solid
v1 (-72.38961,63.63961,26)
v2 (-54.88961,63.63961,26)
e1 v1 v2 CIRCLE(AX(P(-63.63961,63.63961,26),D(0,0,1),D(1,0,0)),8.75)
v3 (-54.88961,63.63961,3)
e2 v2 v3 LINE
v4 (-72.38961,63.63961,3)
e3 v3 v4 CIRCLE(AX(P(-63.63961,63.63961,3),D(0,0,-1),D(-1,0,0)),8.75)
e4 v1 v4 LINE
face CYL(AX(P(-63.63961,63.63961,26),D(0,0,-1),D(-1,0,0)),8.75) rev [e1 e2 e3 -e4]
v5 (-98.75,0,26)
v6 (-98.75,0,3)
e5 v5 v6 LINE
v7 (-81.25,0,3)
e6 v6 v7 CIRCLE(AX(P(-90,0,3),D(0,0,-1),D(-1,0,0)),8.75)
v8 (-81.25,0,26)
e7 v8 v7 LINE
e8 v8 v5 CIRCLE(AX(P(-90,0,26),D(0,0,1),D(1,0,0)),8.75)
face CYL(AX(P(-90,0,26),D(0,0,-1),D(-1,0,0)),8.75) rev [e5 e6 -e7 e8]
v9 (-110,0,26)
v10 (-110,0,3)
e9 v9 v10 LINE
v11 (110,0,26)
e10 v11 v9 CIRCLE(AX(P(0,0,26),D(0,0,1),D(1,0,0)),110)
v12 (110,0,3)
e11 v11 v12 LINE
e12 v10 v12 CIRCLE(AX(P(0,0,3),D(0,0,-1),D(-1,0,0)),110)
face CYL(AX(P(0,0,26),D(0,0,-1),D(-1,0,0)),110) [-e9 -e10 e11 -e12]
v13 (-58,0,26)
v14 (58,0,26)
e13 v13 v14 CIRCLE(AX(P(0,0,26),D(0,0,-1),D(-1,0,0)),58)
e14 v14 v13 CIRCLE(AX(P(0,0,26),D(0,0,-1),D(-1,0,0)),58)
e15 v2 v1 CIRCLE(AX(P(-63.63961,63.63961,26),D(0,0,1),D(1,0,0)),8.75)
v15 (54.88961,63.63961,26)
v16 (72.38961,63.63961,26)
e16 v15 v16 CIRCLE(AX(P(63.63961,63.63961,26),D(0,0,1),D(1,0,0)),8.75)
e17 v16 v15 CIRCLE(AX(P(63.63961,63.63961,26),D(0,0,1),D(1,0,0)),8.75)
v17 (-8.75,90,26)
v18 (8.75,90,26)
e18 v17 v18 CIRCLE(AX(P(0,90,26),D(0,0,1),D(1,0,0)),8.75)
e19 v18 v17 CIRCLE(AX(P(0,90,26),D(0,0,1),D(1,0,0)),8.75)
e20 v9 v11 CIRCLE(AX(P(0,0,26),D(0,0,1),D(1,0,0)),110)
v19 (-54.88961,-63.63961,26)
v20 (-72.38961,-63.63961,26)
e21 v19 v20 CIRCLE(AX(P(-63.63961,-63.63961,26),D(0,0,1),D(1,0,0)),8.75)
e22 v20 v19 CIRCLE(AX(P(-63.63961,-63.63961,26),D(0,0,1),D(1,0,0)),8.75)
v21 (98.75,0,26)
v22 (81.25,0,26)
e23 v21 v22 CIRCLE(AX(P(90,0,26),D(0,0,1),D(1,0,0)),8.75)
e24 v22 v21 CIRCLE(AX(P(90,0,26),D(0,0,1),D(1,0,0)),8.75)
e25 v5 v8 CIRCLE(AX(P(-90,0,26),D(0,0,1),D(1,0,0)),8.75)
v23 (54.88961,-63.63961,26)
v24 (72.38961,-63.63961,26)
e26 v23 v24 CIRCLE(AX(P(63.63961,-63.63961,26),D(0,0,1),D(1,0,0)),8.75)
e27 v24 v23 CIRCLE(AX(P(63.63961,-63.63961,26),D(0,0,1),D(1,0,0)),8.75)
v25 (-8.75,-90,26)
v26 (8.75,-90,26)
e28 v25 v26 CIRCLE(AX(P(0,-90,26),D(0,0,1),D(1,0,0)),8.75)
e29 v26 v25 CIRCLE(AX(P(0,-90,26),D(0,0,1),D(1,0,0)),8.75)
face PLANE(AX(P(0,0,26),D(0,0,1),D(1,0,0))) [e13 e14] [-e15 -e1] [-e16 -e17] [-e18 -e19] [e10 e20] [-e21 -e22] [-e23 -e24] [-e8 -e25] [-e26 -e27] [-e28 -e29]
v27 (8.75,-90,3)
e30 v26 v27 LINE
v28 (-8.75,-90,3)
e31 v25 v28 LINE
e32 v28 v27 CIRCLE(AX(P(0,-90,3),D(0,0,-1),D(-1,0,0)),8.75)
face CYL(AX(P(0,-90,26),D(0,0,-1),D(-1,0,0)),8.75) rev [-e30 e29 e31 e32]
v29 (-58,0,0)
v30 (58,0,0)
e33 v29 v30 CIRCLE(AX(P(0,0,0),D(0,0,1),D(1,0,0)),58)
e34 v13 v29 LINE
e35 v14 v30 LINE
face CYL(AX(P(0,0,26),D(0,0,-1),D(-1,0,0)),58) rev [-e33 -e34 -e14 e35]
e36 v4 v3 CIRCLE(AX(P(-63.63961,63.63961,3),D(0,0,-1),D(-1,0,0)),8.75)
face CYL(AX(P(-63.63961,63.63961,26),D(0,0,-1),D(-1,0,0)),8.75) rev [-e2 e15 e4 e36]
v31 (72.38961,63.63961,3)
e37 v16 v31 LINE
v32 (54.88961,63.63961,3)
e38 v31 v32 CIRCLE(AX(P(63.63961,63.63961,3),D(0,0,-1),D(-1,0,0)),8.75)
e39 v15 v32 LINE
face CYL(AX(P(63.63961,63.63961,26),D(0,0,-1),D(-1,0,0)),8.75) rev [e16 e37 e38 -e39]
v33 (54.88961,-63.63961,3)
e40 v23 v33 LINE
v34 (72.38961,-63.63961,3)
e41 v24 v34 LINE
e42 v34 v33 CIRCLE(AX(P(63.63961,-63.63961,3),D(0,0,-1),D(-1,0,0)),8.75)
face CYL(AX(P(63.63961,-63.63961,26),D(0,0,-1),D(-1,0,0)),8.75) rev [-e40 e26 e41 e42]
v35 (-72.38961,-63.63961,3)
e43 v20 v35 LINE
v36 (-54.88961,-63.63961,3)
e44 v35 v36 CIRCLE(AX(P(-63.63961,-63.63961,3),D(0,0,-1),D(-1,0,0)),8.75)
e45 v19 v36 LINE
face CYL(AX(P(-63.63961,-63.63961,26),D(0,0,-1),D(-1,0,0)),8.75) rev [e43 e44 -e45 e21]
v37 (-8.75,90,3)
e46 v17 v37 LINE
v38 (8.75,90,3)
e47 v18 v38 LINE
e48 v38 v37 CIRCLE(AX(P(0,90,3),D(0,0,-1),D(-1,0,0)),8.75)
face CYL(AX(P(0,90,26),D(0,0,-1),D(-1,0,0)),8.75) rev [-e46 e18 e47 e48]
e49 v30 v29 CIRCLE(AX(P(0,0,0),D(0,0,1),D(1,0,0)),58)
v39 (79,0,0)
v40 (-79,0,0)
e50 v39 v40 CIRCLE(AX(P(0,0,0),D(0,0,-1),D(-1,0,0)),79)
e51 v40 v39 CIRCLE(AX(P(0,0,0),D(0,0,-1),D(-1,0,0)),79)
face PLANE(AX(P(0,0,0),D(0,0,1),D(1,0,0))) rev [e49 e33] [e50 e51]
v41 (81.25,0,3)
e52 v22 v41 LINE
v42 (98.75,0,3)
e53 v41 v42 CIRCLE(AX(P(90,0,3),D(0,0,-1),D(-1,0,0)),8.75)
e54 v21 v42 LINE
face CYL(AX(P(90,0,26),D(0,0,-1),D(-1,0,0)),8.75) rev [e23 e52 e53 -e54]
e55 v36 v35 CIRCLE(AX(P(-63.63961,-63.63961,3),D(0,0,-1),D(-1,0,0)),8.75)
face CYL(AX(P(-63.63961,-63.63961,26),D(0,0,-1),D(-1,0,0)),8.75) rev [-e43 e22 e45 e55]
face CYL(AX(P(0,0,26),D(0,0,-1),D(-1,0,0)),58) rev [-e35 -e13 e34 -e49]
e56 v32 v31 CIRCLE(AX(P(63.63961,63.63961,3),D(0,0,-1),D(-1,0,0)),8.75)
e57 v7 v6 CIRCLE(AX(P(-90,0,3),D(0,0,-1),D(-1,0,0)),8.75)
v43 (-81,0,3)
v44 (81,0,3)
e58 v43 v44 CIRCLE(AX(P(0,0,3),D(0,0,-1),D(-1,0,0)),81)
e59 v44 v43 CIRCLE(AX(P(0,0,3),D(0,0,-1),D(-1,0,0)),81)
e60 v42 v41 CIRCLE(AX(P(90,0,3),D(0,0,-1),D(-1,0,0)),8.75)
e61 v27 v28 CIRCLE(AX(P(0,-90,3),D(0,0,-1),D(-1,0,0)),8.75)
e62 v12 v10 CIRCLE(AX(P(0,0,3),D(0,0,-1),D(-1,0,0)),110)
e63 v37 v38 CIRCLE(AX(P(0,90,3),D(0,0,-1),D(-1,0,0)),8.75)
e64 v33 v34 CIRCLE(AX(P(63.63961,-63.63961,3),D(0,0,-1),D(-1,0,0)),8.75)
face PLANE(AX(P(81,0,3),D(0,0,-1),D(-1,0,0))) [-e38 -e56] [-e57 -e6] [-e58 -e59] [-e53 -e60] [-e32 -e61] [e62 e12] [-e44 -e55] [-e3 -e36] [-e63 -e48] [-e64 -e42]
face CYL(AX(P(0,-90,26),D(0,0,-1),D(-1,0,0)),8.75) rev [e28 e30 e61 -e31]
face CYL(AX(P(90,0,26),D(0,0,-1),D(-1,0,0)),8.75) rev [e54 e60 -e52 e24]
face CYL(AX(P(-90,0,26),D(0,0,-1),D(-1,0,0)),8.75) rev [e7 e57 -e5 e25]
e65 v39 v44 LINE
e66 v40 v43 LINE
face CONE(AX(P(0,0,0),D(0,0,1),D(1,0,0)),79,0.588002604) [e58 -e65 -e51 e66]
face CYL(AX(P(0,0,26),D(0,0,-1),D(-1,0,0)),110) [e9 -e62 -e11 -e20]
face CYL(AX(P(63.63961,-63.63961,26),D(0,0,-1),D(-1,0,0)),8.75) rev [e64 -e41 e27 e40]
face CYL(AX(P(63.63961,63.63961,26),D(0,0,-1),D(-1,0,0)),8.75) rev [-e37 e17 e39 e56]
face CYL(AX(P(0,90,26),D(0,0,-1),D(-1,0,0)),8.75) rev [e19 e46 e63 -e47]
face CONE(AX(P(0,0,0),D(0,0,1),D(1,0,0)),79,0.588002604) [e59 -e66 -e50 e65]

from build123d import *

# Parameters (mm, degrees)
SKETCH1_R               = 110
SKETCH1_R_2             = 8.75
BOSS_EXTRUDE1_DEPTH     = 26
CUT_EXTRUDE1_DEPTH      = 158.721273137
CUT_EXTRUDE1_DEPTH_BACK = 158.721273137
SKETCH4_R               = 58


with BuildPart() as part:
    # Sketch1 → Boss-Extrude1 (new body)
    with BuildSketch(Plane.XY):
        with Locations(Location((0, 0, 0), (0, 0, 180))):
            Circle(SKETCH1_R)
        with Locations(Location((0, 90, 0), (0, 0, 180))):
            Circle(SKETCH1_R_2, mode=Mode.SUBTRACT)
        with Locations(Location((63.639610307, 63.639610307, 0), (0, 0, 180))):
            Circle(SKETCH1_R_2, mode=Mode.SUBTRACT)
        with Locations(Location((90, 0, 0), (0, 0, 180))):
            Circle(SKETCH1_R_2, mode=Mode.SUBTRACT)
        with Locations(Location((63.639610307, -63.639610307, 0), (0, 0, 180))):
            Circle(SKETCH1_R_2, mode=Mode.SUBTRACT)
        with Locations(Location((0, -90, 0), (0, 0, 180))):
            Circle(SKETCH1_R_2, mode=Mode.SUBTRACT)
        with Locations(Location((-63.639610307, -63.639610307, 0), (0, 0, 180))):
            Circle(SKETCH1_R_2, mode=Mode.SUBTRACT)
        with Locations(Location((-90, 0, 0), (0, 0, 180))):
            Circle(SKETCH1_R_2, mode=Mode.SUBTRACT)
        with Locations(Location((-63.639610307, 63.639610307, 0), (0, 0, 180))):
            Circle(SKETCH1_R_2, mode=Mode.SUBTRACT)
    extrude(amount=BOSS_EXTRUDE1_DEPTH)

    # Sketch3 → Cut-Revolve1 (revolve, cut)
    with BuildSketch(Plane(origin=(0, 0, 0), x_dir=(1, 0, 0), z_dir=(0, 1, 0)), mode=Mode.PRIVATE) as cut_revolve1_sk:
        Polygon((81, 0), (79, 0), (81, -3), (110, -3), (110, 0), align=None)
    revolve(cut_revolve1_sk.sketch.rotate(Axis((0, 0, 0), (0, 0, 1)), 180), axis=Axis((0, 0, 0), (0, 0, 1)), mode=Mode.SUBTRACT)

    # Sketch4 → Cut-Extrude1 (cut, two sides: drawn at the far end of the back side and taken through both)
    with BuildSketch(Plane(origin=(0, 0, 0), x_dir=(-1, 0, 0), z_dir=(0, 0, -1)).offset(-CUT_EXTRUDE1_DEPTH_BACK)):
        Circle(SKETCH4_R)
    extrude(amount=CUT_EXTRUDE1_DEPTH + CUT_EXTRUDE1_DEPTH_BACK, mode=Mode.SUBTRACT)


solid = part.part
